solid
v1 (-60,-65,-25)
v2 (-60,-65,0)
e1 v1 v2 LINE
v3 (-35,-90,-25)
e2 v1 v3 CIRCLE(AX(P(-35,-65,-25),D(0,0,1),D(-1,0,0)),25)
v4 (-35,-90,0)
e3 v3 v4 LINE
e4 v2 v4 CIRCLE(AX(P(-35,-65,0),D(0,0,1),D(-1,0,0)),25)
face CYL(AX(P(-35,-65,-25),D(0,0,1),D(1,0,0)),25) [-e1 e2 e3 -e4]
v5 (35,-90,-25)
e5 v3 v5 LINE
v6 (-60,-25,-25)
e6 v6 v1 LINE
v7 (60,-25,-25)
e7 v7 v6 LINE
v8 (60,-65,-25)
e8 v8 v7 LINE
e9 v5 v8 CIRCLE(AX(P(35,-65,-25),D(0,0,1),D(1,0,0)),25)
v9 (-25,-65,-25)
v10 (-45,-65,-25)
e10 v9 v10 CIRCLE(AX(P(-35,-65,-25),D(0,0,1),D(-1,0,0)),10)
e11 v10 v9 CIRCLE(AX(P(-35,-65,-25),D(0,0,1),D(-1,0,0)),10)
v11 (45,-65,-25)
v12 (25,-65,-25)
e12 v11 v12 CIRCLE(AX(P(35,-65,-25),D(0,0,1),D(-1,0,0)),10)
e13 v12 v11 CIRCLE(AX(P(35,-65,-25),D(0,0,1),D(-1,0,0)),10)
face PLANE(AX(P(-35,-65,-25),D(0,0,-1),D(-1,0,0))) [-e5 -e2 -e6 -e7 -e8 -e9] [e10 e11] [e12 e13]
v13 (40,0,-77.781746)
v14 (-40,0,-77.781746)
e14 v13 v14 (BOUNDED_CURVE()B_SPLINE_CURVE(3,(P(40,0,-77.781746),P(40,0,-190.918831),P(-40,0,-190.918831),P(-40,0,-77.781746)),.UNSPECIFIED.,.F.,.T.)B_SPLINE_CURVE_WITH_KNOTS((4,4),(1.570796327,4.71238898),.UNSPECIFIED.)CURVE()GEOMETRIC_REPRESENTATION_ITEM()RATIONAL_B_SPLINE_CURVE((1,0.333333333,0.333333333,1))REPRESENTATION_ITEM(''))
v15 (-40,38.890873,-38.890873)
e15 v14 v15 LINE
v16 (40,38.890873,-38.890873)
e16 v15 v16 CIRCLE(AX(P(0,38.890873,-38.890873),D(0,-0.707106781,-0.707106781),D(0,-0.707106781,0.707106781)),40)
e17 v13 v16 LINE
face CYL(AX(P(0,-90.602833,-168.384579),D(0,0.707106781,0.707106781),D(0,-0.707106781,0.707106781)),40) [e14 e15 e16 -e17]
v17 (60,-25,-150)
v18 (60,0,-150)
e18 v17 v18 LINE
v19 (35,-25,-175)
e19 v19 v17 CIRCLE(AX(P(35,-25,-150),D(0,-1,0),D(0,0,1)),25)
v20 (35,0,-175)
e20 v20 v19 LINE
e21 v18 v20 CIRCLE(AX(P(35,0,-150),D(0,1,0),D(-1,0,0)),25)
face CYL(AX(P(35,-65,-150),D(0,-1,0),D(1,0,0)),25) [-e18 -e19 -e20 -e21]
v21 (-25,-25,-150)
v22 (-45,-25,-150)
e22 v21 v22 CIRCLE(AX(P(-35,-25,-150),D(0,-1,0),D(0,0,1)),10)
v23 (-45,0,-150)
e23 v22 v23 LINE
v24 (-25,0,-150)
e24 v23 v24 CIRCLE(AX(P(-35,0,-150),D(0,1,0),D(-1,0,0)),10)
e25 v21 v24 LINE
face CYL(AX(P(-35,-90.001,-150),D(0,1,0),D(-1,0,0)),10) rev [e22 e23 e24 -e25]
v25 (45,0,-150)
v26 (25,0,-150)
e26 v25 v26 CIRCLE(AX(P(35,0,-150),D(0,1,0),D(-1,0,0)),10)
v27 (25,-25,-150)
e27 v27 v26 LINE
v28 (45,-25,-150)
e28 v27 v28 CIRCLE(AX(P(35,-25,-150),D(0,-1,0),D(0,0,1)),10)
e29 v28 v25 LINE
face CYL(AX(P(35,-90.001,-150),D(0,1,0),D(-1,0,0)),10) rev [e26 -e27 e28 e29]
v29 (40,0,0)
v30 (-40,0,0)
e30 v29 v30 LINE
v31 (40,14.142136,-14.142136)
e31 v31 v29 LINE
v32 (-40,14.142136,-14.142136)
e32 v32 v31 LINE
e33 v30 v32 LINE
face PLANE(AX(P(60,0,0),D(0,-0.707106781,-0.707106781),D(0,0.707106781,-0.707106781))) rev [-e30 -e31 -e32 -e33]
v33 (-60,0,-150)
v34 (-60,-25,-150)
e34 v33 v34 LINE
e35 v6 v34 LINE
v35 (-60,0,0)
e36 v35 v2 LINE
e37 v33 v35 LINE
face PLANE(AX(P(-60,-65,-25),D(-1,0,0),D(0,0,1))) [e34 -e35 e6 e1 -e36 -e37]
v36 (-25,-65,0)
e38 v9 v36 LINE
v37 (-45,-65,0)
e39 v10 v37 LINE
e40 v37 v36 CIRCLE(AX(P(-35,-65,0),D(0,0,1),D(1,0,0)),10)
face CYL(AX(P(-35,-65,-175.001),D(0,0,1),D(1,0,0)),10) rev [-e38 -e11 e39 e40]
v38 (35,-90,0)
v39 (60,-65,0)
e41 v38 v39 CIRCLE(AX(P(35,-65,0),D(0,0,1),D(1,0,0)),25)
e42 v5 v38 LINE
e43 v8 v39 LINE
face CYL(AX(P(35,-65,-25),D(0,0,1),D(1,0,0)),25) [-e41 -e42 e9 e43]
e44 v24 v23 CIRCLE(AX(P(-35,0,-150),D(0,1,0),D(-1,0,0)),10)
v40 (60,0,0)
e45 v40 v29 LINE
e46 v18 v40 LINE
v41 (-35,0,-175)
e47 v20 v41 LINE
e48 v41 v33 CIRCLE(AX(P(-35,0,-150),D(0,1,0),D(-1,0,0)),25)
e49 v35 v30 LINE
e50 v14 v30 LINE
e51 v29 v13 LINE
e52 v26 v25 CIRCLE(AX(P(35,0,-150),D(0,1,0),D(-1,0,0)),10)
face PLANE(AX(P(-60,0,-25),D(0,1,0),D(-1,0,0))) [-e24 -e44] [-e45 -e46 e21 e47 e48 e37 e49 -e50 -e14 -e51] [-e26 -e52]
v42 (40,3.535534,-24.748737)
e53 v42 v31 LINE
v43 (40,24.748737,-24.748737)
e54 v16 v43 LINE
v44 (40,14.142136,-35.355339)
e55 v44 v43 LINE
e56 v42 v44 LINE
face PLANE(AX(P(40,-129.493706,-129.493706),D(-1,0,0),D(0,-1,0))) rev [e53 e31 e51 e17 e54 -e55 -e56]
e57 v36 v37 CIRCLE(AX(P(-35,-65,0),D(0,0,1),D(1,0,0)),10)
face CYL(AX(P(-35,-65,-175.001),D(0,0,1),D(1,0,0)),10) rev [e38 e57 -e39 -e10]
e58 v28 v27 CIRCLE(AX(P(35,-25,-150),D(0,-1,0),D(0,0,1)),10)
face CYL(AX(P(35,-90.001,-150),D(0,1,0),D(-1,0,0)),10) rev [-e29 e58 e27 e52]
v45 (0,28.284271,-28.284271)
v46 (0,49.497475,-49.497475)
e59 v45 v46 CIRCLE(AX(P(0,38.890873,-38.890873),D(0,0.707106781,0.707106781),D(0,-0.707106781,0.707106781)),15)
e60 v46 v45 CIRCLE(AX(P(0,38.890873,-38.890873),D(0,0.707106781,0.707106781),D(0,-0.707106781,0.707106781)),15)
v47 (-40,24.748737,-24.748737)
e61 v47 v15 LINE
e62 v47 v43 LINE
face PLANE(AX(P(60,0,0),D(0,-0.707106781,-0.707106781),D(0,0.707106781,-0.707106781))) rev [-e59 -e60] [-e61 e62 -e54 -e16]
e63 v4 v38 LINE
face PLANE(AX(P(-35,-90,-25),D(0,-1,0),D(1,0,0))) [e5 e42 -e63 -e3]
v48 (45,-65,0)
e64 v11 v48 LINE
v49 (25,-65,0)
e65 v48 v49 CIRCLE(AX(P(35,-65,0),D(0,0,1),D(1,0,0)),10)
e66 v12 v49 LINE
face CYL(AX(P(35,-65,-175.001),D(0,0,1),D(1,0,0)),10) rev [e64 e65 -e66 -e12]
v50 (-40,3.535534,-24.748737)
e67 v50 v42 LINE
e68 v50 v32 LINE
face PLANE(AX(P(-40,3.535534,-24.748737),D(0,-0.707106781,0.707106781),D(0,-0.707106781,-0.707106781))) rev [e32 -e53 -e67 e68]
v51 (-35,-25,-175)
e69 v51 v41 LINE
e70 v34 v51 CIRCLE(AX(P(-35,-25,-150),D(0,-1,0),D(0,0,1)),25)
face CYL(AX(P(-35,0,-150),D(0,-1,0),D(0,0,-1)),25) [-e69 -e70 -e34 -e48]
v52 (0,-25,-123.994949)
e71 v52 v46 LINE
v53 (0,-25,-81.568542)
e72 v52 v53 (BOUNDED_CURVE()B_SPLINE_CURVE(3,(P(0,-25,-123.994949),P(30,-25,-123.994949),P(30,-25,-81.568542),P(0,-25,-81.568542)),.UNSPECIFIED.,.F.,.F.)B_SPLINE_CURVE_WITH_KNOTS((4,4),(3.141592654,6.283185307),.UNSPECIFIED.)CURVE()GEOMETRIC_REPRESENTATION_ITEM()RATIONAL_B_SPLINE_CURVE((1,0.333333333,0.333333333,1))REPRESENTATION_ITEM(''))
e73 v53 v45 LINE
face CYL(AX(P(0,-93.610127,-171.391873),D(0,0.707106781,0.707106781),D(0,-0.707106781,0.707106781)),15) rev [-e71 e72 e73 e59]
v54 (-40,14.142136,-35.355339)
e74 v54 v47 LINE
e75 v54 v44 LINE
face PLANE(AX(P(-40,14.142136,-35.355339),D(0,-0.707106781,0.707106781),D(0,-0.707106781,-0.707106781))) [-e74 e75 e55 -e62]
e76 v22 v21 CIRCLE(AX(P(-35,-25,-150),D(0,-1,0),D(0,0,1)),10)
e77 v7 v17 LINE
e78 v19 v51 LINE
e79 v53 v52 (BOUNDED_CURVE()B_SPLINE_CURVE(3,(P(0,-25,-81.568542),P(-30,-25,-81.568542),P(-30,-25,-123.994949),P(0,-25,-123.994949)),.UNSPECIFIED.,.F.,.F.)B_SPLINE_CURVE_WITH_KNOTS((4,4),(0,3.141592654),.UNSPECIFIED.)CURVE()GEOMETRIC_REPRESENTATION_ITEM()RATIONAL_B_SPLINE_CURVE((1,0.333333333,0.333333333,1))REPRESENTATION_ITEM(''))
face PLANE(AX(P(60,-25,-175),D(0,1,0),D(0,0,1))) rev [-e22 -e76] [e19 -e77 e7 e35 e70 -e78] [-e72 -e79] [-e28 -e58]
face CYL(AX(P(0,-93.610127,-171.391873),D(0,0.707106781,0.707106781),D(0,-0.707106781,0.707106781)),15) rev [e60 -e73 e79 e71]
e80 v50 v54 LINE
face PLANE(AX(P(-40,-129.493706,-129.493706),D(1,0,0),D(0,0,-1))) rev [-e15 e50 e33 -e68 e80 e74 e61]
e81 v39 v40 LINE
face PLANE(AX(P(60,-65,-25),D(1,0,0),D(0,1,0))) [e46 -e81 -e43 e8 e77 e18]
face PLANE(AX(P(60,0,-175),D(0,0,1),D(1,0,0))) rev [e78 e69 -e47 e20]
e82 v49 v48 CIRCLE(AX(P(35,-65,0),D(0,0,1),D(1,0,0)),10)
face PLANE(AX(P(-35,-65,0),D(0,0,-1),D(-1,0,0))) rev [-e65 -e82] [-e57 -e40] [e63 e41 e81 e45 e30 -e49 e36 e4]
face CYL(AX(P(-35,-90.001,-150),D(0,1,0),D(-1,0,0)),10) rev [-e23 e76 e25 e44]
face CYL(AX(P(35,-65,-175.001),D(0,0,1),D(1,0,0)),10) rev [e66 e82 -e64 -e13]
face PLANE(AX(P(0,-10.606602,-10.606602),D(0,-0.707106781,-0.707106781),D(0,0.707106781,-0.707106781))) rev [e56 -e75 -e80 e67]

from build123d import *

# Parameters (mm, degrees)
BASE_PLATE_DEPTH            = 25
UPRIGHT_FLANGE_SKETCH_W     = 150
UPRIGHT_FLANGE_SKETCH_H     = 25
UPRIGHT_FLANGE_DEPTH        = 60
BASE_MOUNTING_HOLES_REACH   = 207.73
BASE_HOLES_SKETCH_R         = 10
LUG_SUPPORT_DEPTH           = 60
LUG_CLEARANCE_CUT_REACH     = 207.73
LUG_BORE_30_REACH           = 207.73
LUG_BORE_SKETCH_R           = 15
LUG_SLOT_SKETCH_W           = 80
LUG_SLOT_SKETCH_H           = 15
LUG_SLOT_DEPTH              = 15
FLANGE_CORNER_FILLETS_R25_R = 25
FLANGE_MOUNTING_HOLES_REACH = 207.73
FLANGE_HOLES_SKETCH_R       = 10


with BuildPart() as part:
    # Base Plate Sketch → Base Plate (new body)
    with BuildSketch(Plane.XY):
        with BuildLine():
            Line((-35, -90), (35, -90))
            ThreePointArc((35, -90), (52.67766953, -82.67766953), (60, -65))
            Line((60, -65), (60, 0))
            Line((60, 0), (-60, 0))
            Line((-60, 0), (-60, -65))
            ThreePointArc((-60, -65), (-52.67766953, -82.67766953), (-35, -90))
        make_face()
    extrude(amount=-BASE_PLATE_DEPTH)

    # Upright Flange Sketch → Upright Flange (add, symmetric)
    with BuildSketch(Plane(origin=(0, 0, 0), x_dir=(0, 0, -1), z_dir=(1, 0, 0))):
        with Locations((100, -12.5)):
            Rectangle(UPRIGHT_FLANGE_SKETCH_W, UPRIGHT_FLANGE_SKETCH_H)
    extrude(amount=UPRIGHT_FLANGE_DEPTH, both=True)

    # Base Holes Sketch → Base Mounting Holes (cut, up to next)
    with BuildSketch(Plane.XY, mode=Mode.PRIVATE) as base_mounting_holes_sk1:
        with Locations((35, -65)):
            Circle(BASE_HOLES_SKETCH_R)
    base_mounting_holes_tool1 = extrude(base_mounting_holes_sk1.sketch, amount=-BASE_MOUNTING_HOLES_REACH, mode=Mode.PRIVATE) & part.part
    # Base Holes Sketch → Base Mounting Holes (cut, up to next)
    with BuildSketch(Plane.XY, mode=Mode.PRIVATE) as base_mounting_holes_sk2:
        with Locations((-35, -65)):
            Circle(BASE_HOLES_SKETCH_R)
    base_mounting_holes_tool2 = extrude(base_mounting_holes_sk2.sketch, amount=-BASE_MOUNTING_HOLES_REACH, mode=Mode.PRIVATE) & part.part
    add(base_mounting_holes_tool1.solids().sort_by_distance((35, -65, 0))[0], mode=Mode.SUBTRACT)
    add(base_mounting_holes_tool2.solids().sort_by_distance((-35, -65, 0))[0], mode=Mode.SUBTRACT)

    # Lug Support Sketch → Lug Support (add, symmetric)
    with BuildSketch(Plane(origin=(0, 0, 0), x_dir=(0, 0, -1), z_dir=(1, 0, 0))):
        Polygon((0, 0), (67.175144213, 67.175144213), (134.350288425, 0), align=None)
    extrude(amount=LUG_SUPPORT_DEPTH, both=True)

    # Lug Clearance Cut: up to this face of the body (flat: up to its plane)
    lug_clearance_cut_end = Plane(part.part.faces().sort_by_distance((0, 0, -154.675144213))[0])
    # Lug Clearance Sketch → Lug Clearance Cut (cut, up to the picked face)
    with BuildSketch(Plane(origin=(0, 0, 0), x_dir=(1, 0, 0), z_dir=(0, 0.7071067811865435, 0.7071067811865517)), mode=Mode.PRIVATE) as lug_clearance_cut_sk1:
        with BuildLine():
            Line((40, 55), (40, 0))
            Line((40, 0), (60, 0))
            Line((60, 0), (60, 95))
            Line((60, 95), (-2.46e-07, 95))
            ThreePointArc((-2.46e-07, 95), (28.28427116, 83.284271335), (40, 55))
        make_face()
    lug_clearance_cut_tool1 = split(extrude(lug_clearance_cut_sk1.sketch, amount=-LUG_CLEARANCE_CUT_REACH, mode=Mode.PRIVATE), bisect_by=lug_clearance_cut_end, keep=Keep.BOTH, mode=Mode.PRIVATE)
    # Lug Clearance Sketch → Lug Clearance Cut (cut, up to the picked face)
    with BuildSketch(Plane(origin=(0, 0, 0), x_dir=(1, 0, 0), z_dir=(0, 0.7071067811865435, 0.7071067811865517)), mode=Mode.PRIVATE) as lug_clearance_cut_sk2:
        with BuildLine():
            Line((-60, 0), (-40, 0))
            Line((-40, 0), (-40, 55))
            ThreePointArc((-40, 55), (-28.284271335, 83.28427116), (-2.46e-07, 95))
            Line((-2.46e-07, 95), (-60, 95))
            Line((-60, 95), (-60, 0))
        make_face()
    lug_clearance_cut_tool2 = split(extrude(lug_clearance_cut_sk2.sketch, amount=-LUG_CLEARANCE_CUT_REACH, mode=Mode.PRIVATE), bisect_by=lug_clearance_cut_end, keep=Keep.BOTH, mode=Mode.PRIVATE)
    add(lug_clearance_cut_tool1.solids().sort_by(Axis((47.101904, 37.761408, -37.761408), (0, -0.7071067811865435, -0.7071067811865517)))[0], mode=Mode.SUBTRACT)
    add(lug_clearance_cut_tool2.solids().sort_by(Axis((-47.101904, 37.761408, -37.761408), (0, -0.7071067811865435, -0.7071067811865517)))[0], mode=Mode.SUBTRACT)

    # Lug Bore Ø30: up to this plane
    lug_bore_30_end = Plane(origin=(60, -25, -175), z_dir=(0, 1, 0))
    # Lug Bore Sketch → Lug Bore Ø30 (cut, up to the surface)
    with BuildSketch(Plane(origin=(0, 0, 0), x_dir=(1, 0, 0), z_dir=(0, 0.7071067811865435, 0.7071067811865517)), mode=Mode.PRIVATE) as lug_bore_30_sk1:
        with Locations(Location((0, 55, 0), (0, 0, 270))):
            Circle(LUG_BORE_SKETCH_R)
    lug_bore_30_tool1 = split(extrude(lug_bore_30_sk1.sketch, amount=-LUG_BORE_30_REACH, mode=Mode.PRIVATE), bisect_by=lug_bore_30_end, keep=Keep.BOTH, mode=Mode.PRIVATE)
    add(lug_bore_30_tool1.solids().sort_by_distance((0, 38.890873, -38.890873))[0], mode=Mode.SUBTRACT)

    # Lug Slot Sketch → Lug Slot (cut)
    with BuildSketch(Plane(origin=(0, 0, 0), x_dir=(1, 0, 0), z_dir=(0, 0.7071067811865435, 0.7071067811865517))):
        with Locations((0, 27.5)):
            Rectangle(LUG_SLOT_SKETCH_W, LUG_SLOT_SKETCH_H)
    extrude(amount=-LUG_SLOT_DEPTH, mode=Mode.SUBTRACT)

    # Flange Corner Fillets R25
    flange_corner_fillets_r25_edges = [part.edges().sort_by_distance(p)[0] for p in [
        (-60, -12.5, -175),
        (60, -12.5, -175),
    ]]
    fillet(flange_corner_fillets_r25_edges, radius=FLANGE_CORNER_FILLETS_R25_R)

    # Flange Holes Sketch → Flange Mounting Holes (cut, up to next)
    with BuildSketch(Plane(origin=(0, 0, 0), x_dir=(1, 0, 0), z_dir=(0, 1, 0)), mode=Mode.PRIVATE) as flange_mounting_holes_sk1:
        with Locations(Location((-35, 150, 0), (0, 0, 180))):
            Circle(FLANGE_HOLES_SKETCH_R)
    flange_mounting_holes_tool1 = extrude(flange_mounting_holes_sk1.sketch, amount=-FLANGE_MOUNTING_HOLES_REACH, mode=Mode.PRIVATE) & part.part
    # Flange Holes Sketch → Flange Mounting Holes (cut, up to next)
    with BuildSketch(Plane(origin=(0, 0, 0), x_dir=(1, 0, 0), z_dir=(0, 1, 0)), mode=Mode.PRIVATE) as flange_mounting_holes_sk2:
        with Locations(Location((35, 150, 0), (0, 0, 180))):
            Circle(FLANGE_HOLES_SKETCH_R)
    flange_mounting_holes_tool2 = extrude(flange_mounting_holes_sk2.sketch, amount=-FLANGE_MOUNTING_HOLES_REACH, mode=Mode.PRIVATE) & part.part
    add(flange_mounting_holes_tool1.solids().sort_by_distance((-35, 0, -150))[0], mode=Mode.SUBTRACT)
    add(flange_mounting_holes_tool2.solids().sort_by_distance((35, 0, -150))[0], mode=Mode.SUBTRACT)


solid = part.part
